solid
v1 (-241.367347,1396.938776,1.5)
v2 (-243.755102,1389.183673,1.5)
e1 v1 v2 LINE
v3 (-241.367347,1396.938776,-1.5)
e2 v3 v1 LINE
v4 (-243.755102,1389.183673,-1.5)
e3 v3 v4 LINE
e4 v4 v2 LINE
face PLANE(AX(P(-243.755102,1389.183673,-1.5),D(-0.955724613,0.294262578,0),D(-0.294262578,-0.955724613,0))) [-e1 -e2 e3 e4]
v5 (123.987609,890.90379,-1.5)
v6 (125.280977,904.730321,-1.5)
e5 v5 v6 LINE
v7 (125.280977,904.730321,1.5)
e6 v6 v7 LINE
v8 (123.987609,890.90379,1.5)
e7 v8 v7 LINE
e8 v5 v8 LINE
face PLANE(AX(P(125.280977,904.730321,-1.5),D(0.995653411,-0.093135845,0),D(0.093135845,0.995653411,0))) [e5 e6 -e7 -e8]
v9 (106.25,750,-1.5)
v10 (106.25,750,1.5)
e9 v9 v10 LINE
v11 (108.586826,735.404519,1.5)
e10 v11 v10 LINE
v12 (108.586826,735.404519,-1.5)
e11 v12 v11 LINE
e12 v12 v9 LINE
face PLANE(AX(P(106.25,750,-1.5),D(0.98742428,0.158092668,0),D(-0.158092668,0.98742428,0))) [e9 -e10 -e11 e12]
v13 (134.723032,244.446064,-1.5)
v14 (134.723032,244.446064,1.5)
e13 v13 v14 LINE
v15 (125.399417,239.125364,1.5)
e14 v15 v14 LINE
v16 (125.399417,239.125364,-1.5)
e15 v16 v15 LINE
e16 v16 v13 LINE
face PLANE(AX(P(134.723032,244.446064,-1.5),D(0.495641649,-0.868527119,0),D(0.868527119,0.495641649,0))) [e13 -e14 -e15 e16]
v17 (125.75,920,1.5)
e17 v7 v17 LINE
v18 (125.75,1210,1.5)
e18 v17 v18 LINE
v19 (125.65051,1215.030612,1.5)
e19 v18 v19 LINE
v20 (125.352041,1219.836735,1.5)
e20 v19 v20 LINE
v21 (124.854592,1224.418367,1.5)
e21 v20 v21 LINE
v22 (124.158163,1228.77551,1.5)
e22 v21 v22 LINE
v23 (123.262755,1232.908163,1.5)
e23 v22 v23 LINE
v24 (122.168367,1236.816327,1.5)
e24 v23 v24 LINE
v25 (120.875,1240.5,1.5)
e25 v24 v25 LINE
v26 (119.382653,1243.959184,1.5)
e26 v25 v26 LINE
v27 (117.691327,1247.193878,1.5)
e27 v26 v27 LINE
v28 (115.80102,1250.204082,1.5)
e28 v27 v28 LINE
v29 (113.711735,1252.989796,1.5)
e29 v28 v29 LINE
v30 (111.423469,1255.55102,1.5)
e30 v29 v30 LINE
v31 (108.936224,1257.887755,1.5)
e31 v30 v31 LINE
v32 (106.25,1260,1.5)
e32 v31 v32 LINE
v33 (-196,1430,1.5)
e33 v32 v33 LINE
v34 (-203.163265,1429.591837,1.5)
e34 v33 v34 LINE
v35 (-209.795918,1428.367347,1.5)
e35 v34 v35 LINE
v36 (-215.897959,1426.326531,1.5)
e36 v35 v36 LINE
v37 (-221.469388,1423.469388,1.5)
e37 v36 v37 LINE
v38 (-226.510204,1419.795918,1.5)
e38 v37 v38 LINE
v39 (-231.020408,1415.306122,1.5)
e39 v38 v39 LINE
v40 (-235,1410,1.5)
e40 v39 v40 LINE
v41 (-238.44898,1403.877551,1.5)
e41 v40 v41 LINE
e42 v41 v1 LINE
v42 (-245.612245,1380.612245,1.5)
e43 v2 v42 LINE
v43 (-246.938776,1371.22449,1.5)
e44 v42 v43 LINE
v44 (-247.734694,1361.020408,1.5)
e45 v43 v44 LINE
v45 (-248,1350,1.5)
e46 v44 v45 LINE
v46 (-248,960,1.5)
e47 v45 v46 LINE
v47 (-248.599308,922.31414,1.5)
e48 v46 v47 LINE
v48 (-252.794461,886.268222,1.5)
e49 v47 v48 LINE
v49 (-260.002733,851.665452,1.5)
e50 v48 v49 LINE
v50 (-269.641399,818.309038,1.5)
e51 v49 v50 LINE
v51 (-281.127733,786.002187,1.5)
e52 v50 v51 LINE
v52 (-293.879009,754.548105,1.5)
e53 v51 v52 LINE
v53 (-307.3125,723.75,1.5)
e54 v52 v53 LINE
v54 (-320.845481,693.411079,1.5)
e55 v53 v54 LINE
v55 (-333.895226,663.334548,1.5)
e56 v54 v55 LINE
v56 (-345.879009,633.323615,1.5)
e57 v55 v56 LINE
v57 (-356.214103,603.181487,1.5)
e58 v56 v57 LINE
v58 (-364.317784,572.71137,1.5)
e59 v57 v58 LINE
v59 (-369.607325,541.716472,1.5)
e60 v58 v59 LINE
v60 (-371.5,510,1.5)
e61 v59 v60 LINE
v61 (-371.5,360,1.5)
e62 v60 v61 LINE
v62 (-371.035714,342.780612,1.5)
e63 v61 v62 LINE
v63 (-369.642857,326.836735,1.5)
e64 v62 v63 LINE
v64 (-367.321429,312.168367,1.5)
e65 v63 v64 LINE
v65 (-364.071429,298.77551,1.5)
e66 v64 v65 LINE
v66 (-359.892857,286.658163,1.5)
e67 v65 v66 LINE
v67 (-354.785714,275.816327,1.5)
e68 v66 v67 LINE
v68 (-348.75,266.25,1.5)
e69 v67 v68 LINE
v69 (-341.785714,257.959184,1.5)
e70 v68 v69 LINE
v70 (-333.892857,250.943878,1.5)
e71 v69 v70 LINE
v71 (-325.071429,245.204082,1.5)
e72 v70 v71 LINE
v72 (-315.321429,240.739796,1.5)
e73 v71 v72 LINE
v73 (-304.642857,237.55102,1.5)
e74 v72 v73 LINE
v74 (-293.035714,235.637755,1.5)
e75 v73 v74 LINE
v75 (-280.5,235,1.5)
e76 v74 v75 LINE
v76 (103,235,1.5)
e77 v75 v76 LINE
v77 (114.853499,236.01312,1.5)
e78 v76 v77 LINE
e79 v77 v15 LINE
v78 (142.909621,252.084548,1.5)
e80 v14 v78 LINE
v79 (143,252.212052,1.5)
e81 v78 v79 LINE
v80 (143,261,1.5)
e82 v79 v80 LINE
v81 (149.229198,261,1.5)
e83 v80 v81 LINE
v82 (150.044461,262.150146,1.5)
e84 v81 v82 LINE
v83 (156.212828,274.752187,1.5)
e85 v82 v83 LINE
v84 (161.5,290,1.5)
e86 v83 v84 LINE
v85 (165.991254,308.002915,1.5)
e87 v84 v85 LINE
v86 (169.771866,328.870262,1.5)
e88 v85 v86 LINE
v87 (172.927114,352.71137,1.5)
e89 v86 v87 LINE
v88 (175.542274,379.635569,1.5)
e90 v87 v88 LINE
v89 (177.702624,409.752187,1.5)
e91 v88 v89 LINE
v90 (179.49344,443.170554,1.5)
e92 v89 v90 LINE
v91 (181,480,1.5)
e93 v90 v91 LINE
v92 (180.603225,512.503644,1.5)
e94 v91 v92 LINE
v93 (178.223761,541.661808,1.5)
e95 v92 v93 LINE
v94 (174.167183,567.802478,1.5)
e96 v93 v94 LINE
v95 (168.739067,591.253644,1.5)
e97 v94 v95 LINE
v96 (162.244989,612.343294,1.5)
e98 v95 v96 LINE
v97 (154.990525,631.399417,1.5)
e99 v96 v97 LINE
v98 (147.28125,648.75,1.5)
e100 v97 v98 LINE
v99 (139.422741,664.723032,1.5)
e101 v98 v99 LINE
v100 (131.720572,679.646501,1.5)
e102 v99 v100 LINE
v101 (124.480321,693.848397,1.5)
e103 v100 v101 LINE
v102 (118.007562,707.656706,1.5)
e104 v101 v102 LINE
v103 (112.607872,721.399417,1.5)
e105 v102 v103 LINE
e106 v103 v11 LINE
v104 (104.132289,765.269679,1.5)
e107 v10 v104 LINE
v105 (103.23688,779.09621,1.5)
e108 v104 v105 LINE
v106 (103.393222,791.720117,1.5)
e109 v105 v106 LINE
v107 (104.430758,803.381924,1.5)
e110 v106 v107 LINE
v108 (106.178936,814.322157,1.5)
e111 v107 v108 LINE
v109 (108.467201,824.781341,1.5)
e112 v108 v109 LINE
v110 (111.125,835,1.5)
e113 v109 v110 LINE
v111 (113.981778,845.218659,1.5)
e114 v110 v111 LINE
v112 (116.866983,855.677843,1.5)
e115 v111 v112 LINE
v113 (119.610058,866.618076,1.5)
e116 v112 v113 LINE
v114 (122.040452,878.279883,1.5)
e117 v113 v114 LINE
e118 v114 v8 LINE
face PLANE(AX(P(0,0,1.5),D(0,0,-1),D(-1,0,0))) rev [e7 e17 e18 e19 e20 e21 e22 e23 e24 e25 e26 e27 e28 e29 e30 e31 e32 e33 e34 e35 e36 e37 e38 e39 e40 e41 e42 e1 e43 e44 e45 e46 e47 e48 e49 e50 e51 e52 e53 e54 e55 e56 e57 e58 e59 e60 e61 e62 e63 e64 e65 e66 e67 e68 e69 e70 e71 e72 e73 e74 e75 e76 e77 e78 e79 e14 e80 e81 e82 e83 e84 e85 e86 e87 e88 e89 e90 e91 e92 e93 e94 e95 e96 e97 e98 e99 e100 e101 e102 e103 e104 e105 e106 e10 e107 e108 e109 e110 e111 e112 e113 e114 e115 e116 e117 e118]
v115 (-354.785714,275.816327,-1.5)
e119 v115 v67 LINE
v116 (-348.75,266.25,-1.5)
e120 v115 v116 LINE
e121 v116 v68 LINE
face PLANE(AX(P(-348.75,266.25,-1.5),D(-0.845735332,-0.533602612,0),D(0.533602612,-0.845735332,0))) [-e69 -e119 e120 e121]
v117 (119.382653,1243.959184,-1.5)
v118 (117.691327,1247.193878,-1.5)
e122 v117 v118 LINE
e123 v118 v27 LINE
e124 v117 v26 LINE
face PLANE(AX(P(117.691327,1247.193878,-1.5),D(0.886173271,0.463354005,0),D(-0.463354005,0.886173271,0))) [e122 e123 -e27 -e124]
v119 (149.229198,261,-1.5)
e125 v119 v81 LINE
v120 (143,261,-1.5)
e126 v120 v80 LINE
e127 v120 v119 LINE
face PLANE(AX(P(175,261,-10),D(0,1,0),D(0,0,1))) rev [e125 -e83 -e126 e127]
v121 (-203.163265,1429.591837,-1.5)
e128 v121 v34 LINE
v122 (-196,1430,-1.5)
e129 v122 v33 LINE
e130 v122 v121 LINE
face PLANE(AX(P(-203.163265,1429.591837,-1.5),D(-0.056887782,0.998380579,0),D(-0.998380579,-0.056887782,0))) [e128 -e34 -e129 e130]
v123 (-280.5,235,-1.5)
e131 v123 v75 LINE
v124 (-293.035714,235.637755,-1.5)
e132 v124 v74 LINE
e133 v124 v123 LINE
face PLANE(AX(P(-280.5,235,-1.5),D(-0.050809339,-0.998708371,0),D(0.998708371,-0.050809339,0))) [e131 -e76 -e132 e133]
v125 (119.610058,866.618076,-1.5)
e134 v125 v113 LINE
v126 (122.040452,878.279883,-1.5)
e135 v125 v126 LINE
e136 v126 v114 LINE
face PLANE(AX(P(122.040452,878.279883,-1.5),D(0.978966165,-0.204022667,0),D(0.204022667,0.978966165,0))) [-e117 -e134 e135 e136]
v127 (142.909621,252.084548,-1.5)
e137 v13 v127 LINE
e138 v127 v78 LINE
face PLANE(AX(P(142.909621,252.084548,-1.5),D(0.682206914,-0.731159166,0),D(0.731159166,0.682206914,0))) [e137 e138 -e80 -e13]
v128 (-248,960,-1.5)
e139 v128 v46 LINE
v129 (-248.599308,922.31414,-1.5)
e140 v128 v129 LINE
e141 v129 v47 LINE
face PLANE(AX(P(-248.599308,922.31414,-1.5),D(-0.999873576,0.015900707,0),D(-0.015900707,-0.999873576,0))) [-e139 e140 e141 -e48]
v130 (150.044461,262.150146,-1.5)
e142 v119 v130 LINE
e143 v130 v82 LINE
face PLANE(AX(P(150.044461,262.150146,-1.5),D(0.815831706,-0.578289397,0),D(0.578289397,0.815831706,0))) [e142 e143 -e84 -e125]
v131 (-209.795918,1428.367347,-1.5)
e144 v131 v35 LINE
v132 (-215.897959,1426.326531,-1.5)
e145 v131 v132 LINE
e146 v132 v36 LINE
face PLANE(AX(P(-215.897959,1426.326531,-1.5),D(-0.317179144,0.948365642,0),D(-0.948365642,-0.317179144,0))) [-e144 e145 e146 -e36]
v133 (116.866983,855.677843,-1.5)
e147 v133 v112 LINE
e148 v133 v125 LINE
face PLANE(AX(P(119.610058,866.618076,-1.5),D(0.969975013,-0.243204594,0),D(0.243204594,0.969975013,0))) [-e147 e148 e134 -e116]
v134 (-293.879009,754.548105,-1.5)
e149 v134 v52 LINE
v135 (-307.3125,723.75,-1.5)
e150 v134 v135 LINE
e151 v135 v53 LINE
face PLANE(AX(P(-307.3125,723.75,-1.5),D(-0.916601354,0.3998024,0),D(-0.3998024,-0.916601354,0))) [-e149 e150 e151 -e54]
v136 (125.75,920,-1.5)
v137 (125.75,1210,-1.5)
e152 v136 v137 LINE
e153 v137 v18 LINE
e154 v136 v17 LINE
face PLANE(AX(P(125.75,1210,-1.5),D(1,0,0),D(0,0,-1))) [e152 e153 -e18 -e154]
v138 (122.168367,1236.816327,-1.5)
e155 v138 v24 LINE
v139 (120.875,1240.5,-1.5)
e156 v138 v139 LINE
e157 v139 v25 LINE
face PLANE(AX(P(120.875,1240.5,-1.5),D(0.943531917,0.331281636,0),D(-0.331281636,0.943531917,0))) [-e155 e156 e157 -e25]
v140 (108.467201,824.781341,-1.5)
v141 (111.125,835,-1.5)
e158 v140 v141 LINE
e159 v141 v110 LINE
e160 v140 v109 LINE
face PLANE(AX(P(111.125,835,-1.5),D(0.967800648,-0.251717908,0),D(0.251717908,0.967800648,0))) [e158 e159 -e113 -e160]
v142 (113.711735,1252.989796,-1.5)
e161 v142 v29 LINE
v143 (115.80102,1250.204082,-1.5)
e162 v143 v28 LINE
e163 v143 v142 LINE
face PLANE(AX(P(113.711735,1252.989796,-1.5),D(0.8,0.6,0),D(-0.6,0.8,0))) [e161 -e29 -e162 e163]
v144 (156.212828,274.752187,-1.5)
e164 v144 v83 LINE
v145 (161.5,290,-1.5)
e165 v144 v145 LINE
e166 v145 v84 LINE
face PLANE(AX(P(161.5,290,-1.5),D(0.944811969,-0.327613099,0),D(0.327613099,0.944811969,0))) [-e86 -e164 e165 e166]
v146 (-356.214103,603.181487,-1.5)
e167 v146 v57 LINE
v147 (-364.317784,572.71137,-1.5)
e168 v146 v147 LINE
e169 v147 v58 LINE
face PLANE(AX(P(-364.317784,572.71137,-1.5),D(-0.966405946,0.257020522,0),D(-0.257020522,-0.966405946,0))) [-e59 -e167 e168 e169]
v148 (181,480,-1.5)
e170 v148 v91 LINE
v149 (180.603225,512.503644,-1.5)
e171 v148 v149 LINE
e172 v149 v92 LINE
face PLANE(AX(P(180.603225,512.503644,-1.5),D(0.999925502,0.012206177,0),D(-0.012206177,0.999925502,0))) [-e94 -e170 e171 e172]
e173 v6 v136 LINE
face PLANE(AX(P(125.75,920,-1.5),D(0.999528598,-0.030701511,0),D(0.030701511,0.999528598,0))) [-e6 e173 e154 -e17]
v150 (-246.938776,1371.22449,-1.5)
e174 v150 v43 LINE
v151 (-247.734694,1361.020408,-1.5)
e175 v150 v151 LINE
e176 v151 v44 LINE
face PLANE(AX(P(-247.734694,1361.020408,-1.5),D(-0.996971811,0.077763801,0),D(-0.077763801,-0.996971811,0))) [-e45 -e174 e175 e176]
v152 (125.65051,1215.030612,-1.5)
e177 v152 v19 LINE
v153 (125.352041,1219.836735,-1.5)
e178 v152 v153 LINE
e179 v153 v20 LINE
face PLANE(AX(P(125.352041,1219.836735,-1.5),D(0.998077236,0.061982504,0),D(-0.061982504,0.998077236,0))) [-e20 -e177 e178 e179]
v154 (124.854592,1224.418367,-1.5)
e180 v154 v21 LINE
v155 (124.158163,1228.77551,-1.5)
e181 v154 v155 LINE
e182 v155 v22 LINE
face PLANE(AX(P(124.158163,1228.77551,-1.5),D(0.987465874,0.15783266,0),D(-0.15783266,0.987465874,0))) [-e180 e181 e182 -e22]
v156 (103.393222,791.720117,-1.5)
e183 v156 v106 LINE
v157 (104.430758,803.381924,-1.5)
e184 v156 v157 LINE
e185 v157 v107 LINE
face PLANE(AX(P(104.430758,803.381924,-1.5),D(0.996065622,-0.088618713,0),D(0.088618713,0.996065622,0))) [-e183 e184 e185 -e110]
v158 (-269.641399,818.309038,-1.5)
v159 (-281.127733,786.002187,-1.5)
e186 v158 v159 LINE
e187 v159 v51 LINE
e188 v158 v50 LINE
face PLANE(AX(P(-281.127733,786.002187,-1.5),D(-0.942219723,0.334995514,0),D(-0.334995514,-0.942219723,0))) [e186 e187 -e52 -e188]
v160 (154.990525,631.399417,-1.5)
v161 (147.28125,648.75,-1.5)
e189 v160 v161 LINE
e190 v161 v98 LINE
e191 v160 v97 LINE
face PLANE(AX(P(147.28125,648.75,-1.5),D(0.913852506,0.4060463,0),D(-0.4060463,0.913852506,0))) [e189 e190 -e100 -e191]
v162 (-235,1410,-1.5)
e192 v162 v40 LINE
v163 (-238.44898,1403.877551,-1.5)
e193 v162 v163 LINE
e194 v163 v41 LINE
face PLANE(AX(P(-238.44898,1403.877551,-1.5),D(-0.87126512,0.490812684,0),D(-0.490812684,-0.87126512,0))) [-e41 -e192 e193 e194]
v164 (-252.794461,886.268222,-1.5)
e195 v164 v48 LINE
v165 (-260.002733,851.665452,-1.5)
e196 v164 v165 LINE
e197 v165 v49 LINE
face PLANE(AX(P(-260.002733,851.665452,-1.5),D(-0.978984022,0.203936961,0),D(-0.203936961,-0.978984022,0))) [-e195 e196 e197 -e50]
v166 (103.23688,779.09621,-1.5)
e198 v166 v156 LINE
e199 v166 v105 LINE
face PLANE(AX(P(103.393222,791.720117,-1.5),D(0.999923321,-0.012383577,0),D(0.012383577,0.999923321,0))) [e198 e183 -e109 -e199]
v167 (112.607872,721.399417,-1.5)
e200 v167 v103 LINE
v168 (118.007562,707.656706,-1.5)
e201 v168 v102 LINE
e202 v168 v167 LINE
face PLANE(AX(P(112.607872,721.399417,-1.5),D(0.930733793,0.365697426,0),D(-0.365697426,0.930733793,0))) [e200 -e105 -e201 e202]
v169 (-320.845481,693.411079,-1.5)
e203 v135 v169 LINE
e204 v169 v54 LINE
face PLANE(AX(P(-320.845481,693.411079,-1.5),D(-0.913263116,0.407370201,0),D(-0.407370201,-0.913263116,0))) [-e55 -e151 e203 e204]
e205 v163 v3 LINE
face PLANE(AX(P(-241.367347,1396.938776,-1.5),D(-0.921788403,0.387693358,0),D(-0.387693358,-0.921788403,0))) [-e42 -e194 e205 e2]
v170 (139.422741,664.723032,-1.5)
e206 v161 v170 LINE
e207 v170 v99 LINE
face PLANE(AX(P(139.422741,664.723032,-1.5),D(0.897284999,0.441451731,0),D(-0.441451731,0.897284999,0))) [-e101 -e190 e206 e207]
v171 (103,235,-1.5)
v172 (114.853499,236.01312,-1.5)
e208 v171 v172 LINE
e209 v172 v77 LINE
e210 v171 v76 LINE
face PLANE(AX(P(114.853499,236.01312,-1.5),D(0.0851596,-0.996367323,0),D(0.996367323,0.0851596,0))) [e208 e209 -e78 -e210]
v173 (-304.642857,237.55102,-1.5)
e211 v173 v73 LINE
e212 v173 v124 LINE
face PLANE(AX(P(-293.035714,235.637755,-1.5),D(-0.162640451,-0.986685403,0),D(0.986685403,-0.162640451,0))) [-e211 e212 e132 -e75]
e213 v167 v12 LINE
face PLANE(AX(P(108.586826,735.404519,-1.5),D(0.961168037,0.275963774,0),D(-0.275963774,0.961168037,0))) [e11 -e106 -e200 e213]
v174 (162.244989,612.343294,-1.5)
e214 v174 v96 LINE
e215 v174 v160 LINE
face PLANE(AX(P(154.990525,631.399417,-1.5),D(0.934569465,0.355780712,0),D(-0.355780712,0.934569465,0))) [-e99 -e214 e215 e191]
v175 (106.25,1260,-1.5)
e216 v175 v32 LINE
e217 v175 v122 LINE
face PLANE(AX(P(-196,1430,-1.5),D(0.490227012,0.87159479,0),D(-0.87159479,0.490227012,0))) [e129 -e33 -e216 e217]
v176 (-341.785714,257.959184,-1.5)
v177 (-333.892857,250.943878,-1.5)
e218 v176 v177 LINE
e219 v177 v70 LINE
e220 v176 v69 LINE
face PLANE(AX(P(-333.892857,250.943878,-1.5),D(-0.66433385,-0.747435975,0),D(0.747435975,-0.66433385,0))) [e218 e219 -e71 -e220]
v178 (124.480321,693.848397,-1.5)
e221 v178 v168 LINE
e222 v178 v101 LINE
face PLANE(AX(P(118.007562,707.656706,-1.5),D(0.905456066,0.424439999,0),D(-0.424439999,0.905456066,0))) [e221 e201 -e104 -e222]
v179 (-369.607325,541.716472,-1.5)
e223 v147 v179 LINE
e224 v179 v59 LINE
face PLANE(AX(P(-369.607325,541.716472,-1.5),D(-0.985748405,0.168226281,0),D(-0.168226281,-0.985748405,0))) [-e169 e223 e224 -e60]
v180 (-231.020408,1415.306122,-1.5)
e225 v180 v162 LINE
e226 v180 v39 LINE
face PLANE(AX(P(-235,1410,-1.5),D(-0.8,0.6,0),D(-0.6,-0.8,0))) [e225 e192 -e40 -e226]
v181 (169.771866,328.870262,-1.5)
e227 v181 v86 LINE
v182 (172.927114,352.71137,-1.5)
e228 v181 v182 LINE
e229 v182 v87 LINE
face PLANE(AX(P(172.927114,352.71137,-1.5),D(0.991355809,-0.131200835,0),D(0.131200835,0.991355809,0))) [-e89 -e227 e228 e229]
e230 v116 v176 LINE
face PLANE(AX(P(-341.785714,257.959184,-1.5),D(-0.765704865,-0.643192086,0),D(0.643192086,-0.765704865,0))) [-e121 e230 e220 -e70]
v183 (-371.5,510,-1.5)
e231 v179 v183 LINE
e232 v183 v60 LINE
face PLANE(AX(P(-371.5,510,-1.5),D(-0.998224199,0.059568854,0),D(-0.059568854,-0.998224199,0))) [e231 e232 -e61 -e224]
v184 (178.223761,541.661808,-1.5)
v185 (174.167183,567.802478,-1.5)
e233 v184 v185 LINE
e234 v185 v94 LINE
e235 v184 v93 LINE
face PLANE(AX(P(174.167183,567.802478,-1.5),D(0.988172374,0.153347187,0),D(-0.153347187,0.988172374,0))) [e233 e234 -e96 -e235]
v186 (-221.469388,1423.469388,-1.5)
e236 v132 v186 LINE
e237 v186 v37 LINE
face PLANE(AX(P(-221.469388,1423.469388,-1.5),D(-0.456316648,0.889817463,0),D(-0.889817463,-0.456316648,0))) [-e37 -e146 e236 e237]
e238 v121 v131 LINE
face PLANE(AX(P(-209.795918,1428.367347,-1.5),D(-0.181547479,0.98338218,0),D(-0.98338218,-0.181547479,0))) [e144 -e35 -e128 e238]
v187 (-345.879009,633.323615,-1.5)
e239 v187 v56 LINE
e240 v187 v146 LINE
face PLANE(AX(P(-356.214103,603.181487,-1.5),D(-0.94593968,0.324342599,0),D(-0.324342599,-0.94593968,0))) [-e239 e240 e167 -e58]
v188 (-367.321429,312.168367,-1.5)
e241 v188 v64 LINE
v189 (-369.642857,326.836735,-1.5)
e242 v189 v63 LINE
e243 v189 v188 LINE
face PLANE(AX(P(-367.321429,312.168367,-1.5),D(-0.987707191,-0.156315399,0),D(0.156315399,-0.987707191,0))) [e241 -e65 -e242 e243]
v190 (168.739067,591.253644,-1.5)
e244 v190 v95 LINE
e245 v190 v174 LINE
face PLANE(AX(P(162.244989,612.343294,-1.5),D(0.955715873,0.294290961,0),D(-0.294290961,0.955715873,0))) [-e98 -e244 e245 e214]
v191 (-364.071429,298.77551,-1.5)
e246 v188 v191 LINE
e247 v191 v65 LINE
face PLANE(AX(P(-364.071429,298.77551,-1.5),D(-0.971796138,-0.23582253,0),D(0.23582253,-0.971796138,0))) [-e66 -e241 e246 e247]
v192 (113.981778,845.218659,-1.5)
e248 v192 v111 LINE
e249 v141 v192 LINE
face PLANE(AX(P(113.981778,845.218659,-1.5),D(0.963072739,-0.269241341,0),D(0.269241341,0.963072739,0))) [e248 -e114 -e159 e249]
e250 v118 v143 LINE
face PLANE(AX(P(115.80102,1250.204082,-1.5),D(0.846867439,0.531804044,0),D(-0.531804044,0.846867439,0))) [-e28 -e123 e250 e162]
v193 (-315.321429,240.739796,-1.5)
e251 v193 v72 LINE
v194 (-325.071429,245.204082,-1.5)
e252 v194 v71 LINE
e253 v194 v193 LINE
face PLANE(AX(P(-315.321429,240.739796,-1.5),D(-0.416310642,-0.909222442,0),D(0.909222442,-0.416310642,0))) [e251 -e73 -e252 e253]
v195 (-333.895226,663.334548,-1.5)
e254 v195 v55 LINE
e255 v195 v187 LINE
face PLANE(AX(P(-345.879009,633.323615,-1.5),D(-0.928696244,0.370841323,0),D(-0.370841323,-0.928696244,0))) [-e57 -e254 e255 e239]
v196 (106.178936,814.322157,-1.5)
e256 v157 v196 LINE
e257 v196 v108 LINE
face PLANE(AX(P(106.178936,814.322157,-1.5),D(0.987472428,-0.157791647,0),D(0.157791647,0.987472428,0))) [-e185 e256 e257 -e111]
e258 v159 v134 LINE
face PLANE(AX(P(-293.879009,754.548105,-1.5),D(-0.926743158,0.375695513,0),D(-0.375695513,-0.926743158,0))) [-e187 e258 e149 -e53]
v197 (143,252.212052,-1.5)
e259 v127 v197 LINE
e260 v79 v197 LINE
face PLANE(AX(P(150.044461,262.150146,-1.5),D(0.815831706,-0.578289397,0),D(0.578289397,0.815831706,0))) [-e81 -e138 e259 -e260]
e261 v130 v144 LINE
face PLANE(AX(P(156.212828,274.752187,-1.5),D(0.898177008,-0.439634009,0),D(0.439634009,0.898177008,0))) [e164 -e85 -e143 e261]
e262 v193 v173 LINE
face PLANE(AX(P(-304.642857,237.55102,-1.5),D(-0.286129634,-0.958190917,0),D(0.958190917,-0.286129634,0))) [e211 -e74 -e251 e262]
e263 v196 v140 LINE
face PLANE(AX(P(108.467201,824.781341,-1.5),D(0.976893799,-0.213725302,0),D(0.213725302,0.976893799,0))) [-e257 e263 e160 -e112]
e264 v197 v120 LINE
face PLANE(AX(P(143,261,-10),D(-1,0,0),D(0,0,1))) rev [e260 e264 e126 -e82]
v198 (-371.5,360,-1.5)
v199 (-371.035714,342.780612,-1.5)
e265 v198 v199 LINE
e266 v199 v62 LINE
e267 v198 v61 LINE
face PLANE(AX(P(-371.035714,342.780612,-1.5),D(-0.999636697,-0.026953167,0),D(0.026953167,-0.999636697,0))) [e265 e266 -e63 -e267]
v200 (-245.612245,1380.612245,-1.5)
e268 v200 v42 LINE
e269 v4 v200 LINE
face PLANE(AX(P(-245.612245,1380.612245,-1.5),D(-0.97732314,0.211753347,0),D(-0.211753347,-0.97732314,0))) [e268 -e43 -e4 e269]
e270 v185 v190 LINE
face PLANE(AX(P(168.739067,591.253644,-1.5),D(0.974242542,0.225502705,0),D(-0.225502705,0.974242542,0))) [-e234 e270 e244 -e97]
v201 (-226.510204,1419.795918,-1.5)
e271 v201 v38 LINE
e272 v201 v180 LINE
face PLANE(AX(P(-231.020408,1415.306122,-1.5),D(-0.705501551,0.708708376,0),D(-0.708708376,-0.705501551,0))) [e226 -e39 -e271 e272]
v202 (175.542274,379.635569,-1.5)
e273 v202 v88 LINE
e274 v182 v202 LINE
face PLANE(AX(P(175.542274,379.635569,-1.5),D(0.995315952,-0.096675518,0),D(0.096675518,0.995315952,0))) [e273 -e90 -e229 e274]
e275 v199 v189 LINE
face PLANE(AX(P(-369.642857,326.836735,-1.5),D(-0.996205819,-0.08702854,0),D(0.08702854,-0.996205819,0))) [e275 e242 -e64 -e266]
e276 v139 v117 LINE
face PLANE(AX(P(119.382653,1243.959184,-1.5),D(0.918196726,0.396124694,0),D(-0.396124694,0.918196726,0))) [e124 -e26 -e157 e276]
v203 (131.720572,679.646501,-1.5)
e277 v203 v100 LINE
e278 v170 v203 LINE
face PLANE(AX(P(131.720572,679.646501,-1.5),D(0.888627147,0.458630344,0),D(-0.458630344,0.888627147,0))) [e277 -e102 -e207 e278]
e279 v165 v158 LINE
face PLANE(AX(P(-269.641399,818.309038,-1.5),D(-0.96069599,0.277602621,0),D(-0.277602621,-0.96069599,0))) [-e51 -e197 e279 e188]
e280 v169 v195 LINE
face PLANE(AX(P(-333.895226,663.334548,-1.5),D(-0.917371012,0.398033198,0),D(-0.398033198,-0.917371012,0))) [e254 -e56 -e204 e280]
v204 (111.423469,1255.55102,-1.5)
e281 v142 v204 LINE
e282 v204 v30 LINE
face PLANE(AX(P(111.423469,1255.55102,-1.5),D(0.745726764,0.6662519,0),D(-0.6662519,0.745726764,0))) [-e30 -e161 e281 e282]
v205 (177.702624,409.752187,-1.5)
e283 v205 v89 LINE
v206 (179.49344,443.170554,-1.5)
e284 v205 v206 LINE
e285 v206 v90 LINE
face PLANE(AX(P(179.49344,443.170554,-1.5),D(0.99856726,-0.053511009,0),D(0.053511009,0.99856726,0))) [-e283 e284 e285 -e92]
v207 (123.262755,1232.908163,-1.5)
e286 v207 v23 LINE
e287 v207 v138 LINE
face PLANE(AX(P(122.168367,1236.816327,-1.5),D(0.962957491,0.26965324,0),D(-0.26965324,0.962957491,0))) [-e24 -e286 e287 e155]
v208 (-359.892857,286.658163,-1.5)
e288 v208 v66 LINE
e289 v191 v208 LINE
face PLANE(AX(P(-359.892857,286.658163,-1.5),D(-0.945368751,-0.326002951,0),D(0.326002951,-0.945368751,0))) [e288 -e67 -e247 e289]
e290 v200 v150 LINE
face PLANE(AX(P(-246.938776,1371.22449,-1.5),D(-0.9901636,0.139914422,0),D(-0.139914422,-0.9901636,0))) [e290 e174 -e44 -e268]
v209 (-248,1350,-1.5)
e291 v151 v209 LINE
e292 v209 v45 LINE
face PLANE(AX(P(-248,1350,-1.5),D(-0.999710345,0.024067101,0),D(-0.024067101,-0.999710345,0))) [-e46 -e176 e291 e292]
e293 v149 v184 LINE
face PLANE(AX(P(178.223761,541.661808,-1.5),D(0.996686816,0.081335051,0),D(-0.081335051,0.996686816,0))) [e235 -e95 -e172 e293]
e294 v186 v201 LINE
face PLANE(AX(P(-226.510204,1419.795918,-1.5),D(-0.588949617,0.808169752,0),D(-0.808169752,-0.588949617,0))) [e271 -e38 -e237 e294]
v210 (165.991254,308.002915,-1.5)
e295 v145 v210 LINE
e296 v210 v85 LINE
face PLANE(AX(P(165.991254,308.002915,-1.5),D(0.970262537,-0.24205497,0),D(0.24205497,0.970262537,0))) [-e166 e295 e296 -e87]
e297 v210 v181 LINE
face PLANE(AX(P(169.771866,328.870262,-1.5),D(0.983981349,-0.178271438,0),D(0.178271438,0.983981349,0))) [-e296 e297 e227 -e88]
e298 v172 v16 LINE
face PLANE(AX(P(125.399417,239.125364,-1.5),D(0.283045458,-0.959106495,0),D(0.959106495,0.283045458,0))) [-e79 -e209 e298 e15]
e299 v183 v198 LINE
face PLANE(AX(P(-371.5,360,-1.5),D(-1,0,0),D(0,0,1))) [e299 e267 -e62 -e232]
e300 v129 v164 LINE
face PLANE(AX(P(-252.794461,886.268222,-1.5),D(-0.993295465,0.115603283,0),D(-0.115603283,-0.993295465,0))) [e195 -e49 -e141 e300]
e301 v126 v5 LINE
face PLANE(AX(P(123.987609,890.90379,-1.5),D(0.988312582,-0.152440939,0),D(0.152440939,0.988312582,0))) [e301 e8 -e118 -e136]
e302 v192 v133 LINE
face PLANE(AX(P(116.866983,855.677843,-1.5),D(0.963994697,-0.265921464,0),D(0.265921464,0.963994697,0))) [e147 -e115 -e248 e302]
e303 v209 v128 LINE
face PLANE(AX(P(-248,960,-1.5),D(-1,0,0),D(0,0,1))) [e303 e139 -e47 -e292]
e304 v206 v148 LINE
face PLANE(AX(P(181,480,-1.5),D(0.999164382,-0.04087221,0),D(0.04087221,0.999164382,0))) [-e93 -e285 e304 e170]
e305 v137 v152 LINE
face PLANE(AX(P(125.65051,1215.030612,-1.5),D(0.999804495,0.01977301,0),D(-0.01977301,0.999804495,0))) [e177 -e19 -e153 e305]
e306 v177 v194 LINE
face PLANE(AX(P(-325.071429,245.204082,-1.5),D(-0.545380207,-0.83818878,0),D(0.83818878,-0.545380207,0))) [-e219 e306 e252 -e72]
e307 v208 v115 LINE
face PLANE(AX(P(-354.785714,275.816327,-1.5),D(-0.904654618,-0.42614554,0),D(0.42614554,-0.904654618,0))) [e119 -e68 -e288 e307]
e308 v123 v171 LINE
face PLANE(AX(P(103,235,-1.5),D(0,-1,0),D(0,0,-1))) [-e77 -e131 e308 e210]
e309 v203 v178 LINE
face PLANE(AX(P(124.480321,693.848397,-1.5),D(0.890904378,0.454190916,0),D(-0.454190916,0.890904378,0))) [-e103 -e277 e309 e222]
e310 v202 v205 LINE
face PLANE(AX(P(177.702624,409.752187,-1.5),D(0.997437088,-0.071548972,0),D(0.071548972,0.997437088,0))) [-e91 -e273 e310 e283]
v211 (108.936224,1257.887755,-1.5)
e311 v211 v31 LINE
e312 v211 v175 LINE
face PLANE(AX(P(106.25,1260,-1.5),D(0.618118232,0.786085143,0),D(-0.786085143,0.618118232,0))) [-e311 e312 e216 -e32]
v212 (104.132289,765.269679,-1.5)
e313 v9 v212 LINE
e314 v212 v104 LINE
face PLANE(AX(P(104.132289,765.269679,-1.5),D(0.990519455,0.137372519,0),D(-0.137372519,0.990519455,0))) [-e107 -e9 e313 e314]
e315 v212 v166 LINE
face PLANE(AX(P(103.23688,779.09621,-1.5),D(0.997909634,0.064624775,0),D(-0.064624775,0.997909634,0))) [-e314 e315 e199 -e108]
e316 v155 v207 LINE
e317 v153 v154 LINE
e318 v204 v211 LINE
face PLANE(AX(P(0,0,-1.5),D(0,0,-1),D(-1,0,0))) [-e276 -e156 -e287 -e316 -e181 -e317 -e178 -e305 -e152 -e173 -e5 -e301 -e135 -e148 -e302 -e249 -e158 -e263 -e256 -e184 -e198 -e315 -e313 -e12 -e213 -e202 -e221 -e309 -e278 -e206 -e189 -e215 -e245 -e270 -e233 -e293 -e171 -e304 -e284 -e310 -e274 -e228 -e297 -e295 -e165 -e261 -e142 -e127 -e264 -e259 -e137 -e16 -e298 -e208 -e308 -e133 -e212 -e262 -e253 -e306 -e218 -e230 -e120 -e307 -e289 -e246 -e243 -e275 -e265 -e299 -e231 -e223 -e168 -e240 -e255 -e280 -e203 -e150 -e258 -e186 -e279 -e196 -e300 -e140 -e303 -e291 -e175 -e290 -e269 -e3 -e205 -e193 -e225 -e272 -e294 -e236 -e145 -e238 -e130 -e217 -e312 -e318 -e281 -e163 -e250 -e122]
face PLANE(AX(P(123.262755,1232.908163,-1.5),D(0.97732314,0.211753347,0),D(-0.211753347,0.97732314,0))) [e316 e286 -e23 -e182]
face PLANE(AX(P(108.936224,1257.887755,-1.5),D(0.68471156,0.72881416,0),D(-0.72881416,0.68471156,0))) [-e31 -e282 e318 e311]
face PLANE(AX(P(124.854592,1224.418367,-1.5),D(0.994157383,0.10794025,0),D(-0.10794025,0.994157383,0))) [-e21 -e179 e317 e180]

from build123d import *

# Parameters (mm, degrees)
EXTRUDE_1_DEPTH     = 1.5
SKETCH_2_W          = 32
SKETCH_2_H          = 22
CUT_EXTRUDE_1_DEPTH = 10


with BuildPart() as part:
    # 草图1 → 凸台-拉伸1 (new, symmetric)
    with BuildSketch(Plane.XY):
        Polygon((103, 235), (-24.833333333, 235), (-152.666666667, 235), (-280.5, 235), (-293.035714286, 235.637755102), (-304.642857143, 237.551020408), (-315.321428571, 240.739795918), (-325.071428571, 245.204081633), (-333.892857143, 250.943877551), (-341.785714286, 257.959183673), (-348.75, 266.25), (-354.785714286, 275.816326531), (-359.892857143, 286.658163265), (-364.071428571, 298.775510204), (-367.321428571, 312.168367347), (-369.642857143, 326.836734694), (-371.035714286, 342.780612245), (-371.5, 360), (-371.5, 410), (-371.5, 460), (-371.5, 510), (-369.607325073, 541.716472303), (-364.317784257, 572.711370262), (-356.214103499, 603.18148688), (-345.879008746, 633.32361516), (-333.895225948, 663.334548105), (-320.84548105, 693.411078717), (-307.3125, 723.75), (-293.879008746, 754.548104956), (-281.127733236, 786.002186589), (-269.641399417, 818.309037901), (-260.002733236, 851.665451895), (-252.794460641, 886.268221574), (-248.59930758, 922.314139942), (-248, 960), (-248, 1090), (-248, 1220), (-248, 1350), (-247.734693878, 1361.020408163), (-246.93877551, 1371.224489796), (-245.612244898, 1380.612244898), (-243.755102041, 1389.183673469), (-241.367346939, 1396.93877551), (-238.448979592, 1403.87755102), (-235, 1410), (-231.020408163, 1415.306122449), (-226.510204082, 1419.795918367), (-221.469387755, 1423.469387755), (-215.897959184, 1426.326530612), (-209.795918367, 1428.367346939), (-203.163265306, 1429.591836735), (-196, 1430), (-95.25, 1373.333333333), (5.5, 1316.666666667), (106.25, 1260), (108.93622449, 1257.887755102), (111.423469388, 1255.551020408), (113.711734694, 1252.989795918), (115.801020408, 1250.204081633), (117.691326531, 1247.193877551), (119.382653061, 1243.959183673), (120.875, 1240.5), (122.168367347, 1236.816326531), (123.262755102, 1232.908163265), (124.158163265, 1228.775510204), (124.854591837, 1224.418367347), (125.352040816, 1219.836734694), (125.650510204, 1215.030612245), (125.75, 1210), (125.75, 1113.333333333), (125.75, 1016.666666667), (125.75, 920), (125.280976676, 904.7303207), (123.987609329, 890.903790087), (122.040451895, 878.279883382), (119.610058309, 866.618075802), (116.866982507, 855.677842566), (113.981778426, 845.218658892), (111.125, 835), (108.467201166, 824.781341108), (106.17893586, 814.322157434), (104.430758017, 803.381924198), (103.393221574, 791.720116618), (103.236880466, 779.096209913), (104.13228863, 765.2696793), (106.25, 750), (108.586825802, 735.40451895), (112.60787172, 721.39941691), (118.007561953, 707.656705539), (124.4803207, 693.848396501), (131.720572157, 679.646501458), (139.422740525, 664.72303207), (147.28125, 648.75), (154.990524781, 631.39941691), (162.244989067, 612.343294461), (168.739067055, 591.253644315), (174.167182945, 567.802478134), (178.223760933, 541.66180758), (180.603225219, 512.503644315), (181, 480), (179.493440233, 443.170553936), (177.702623907, 409.752186589), (175.542274052, 379.635568513), (172.927113703, 352.711370262), (169.771865889, 328.870262391), (165.991253644, 308.002915452), (161.5, 290), (156.212827988, 274.752186589), (150.044460641, 262.150145773), (142.909620991, 252.084548105), (134.72303207, 244.44606414), (125.39941691, 239.125364431), (114.853498542, 236.013119534), align=None)
    extrude(amount=EXTRUDE_1_DEPTH, both=True)

    # 草图2 → 切除-拉伸1 (cut, symmetric)
    with BuildSketch(Plane.XY):
        with Locations((159, 250)):
            Rectangle(SKETCH_2_W, SKETCH_2_H)
        with Locations((159, 1150)):
            Rectangle(SKETCH_2_W, SKETCH_2_H)
    extrude(amount=CUT_EXTRUDE_1_DEPTH, both=True, mode=Mode.SUBTRACT)


solid = part.part
